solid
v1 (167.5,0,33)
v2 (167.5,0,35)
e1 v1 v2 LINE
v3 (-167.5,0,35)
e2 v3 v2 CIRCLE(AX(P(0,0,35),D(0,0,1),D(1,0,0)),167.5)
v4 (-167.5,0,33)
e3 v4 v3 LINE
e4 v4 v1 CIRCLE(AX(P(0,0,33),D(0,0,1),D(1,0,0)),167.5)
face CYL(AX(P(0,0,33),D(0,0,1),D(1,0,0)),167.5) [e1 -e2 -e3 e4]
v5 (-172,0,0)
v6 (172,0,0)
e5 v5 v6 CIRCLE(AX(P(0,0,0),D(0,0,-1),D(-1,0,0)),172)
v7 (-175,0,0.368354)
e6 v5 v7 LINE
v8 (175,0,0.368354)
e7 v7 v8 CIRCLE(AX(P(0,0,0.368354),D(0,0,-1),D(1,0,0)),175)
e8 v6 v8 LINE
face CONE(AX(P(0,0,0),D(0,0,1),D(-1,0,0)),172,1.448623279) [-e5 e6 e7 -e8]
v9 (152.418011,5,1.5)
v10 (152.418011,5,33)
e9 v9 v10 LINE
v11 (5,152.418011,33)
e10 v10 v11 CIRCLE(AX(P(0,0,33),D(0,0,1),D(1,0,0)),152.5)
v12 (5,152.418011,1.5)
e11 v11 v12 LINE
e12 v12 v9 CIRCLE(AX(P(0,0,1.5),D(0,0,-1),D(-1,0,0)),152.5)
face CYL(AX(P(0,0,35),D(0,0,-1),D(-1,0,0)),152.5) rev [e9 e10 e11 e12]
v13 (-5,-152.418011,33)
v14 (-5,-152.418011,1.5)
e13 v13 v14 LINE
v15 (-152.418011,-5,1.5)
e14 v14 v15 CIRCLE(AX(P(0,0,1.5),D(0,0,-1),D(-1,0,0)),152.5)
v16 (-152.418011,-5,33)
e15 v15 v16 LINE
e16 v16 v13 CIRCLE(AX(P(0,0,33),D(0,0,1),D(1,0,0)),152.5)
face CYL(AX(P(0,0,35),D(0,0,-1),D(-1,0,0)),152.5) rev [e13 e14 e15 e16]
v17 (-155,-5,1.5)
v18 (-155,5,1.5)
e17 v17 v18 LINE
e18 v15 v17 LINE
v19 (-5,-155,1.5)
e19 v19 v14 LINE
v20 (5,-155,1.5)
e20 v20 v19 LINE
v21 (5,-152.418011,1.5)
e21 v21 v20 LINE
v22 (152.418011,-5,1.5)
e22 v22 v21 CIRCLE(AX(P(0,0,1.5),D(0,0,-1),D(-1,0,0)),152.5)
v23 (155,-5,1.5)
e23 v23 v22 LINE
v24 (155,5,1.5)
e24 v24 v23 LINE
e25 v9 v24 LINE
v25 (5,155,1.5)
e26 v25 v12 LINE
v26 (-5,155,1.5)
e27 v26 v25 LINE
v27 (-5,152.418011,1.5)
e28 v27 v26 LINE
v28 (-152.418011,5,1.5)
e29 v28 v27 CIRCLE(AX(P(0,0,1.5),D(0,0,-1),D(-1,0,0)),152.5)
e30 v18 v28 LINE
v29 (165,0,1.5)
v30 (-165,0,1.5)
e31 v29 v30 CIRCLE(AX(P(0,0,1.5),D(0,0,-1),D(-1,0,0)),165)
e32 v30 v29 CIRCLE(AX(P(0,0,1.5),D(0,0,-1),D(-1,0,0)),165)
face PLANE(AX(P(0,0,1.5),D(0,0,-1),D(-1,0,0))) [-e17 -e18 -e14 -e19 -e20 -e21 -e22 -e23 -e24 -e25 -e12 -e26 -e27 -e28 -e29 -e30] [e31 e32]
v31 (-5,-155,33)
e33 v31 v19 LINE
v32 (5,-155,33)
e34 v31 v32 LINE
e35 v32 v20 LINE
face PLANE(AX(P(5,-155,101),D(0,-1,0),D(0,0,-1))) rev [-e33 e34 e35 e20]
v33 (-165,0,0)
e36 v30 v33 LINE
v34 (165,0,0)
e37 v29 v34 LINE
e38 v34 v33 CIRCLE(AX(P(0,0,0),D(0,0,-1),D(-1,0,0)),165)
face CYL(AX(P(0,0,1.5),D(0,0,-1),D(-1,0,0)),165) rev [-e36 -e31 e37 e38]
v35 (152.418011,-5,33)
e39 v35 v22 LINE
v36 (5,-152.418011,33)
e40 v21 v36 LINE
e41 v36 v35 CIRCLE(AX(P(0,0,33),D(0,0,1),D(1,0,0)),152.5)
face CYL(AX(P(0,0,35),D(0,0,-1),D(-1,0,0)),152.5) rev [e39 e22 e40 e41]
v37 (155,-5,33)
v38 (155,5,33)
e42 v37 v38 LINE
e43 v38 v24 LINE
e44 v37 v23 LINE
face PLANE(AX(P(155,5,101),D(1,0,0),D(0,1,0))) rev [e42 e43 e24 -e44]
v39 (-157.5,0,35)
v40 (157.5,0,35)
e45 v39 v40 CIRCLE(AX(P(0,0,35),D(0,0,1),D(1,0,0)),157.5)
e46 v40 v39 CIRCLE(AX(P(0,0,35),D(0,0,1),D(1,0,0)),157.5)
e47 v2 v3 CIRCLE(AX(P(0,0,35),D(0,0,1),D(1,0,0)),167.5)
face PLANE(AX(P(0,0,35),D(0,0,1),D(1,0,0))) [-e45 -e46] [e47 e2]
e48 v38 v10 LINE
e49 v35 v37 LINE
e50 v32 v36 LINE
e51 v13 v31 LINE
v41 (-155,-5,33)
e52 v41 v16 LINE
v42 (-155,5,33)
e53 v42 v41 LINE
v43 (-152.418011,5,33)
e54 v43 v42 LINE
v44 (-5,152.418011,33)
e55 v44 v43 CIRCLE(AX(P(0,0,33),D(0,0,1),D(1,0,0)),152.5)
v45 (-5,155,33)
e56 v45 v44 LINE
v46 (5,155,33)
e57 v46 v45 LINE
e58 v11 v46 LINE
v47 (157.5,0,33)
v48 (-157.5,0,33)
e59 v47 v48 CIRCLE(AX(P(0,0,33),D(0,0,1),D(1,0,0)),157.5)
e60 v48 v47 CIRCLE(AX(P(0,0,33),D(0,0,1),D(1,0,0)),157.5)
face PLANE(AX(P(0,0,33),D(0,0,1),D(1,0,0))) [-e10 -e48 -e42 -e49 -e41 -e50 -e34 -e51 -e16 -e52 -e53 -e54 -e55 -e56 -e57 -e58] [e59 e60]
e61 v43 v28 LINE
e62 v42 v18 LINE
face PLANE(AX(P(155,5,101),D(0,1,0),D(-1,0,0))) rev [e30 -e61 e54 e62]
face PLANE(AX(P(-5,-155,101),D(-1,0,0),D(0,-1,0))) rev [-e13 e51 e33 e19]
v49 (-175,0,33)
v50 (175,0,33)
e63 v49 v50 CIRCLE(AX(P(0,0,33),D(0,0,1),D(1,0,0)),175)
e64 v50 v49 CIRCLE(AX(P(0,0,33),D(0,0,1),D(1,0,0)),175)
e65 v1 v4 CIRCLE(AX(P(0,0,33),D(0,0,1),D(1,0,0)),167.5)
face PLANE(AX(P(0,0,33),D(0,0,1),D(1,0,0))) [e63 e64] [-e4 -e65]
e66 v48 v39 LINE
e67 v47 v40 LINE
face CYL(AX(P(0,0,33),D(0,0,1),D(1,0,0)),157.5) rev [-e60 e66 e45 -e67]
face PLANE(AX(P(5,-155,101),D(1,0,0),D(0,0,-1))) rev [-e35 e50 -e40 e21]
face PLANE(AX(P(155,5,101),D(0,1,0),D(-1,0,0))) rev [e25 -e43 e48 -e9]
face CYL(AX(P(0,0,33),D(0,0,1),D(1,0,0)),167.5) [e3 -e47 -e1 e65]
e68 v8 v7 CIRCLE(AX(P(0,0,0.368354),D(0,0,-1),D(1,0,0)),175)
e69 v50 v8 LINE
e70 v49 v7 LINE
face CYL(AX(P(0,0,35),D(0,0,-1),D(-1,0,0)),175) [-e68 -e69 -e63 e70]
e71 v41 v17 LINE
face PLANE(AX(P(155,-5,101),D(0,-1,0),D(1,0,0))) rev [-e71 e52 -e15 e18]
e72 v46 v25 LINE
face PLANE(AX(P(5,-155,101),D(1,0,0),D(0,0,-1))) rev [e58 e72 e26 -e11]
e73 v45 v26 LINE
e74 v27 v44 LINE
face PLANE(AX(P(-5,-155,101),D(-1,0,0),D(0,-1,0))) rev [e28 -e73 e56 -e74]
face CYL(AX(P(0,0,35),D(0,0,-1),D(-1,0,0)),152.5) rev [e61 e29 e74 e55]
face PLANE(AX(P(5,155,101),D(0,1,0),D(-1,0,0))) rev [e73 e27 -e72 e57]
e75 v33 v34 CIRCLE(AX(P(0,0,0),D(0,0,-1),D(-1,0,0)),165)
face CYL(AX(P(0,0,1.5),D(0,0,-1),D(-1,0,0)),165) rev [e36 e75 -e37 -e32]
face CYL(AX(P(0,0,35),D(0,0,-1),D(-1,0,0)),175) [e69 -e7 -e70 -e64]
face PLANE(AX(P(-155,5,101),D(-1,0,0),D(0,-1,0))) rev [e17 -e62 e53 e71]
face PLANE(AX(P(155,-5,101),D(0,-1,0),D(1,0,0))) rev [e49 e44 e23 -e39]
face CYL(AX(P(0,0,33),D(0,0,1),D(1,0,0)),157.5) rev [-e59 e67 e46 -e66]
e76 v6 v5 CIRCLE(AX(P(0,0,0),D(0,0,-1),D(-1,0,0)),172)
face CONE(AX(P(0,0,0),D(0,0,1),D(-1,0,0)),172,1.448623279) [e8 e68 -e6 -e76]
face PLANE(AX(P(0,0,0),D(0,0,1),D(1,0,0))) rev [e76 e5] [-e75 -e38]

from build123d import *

# Parameters (mm, degrees)
SKETCH1_R           = 175
BOSS_EXTRUDE1_DEPTH = 35
CUT_EXTRUDE1_START  = -2
SKETCH2_R           = 175
SKETCH2_R_2         = 167.5
CUT_EXTRUDE1_DEPTH  = 2
SKETCH3_R           = 157.5
CUT_EXTRUDE2_DEPTH  = 2
SKETCH4_R           = 165
CUT_EXTRUDE3_DEPTH  = 1.5
SKETCH5_R           = 152.5
CUT_EXTRUDE4_DEPTH  = 250.744369306
SKETCH7_W           = 10
SKETCH7_H           = 310
CUT_EXTRUDE6_DEPTH  = 99.5
CIRPATTERN1_COUNT   = 4
SKETCH8_OUTSIDE_W   = 2071.968
SKETCH8_OUTSIDE_H   = 2071.968
SKETCH8_OUTSIDE_R   = 172
CUT_EXTRUDE7_DEPTH  = 99.5
CUT_EXTRUDE7_DRAFT  = -83


with BuildPart() as part:
    # Sketch1 → Boss-Extrude1 (new body)
    with BuildSketch(Plane.XY):
        Circle(SKETCH1_R)
    extrude(amount=BOSS_EXTRUDE1_DEPTH)

    # Sketch2 → Cut-Extrude1 (cut)
    with BuildSketch(Plane.XY.offset(35).offset(CUT_EXTRUDE1_START)):
        Circle(SKETCH2_R)
        Circle(SKETCH2_R_2, mode=Mode.SUBTRACT)
    extrude(amount=CUT_EXTRUDE1_DEPTH, mode=Mode.SUBTRACT)

    # Sketch3 → Cut-Extrude2 (cut)
    with BuildSketch(Plane.XY.offset(35)):
        Circle(SKETCH3_R)
    extrude(amount=-CUT_EXTRUDE2_DEPTH, mode=Mode.SUBTRACT)

    # Sketch4 → Cut-Extrude3 (cut)
    with BuildSketch(Plane(origin=(0, 0, 0), x_dir=(-1, 0, 0), z_dir=(0, 0, -1))):
        Circle(SKETCH4_R)
    extrude(amount=-CUT_EXTRUDE3_DEPTH, mode=Mode.SUBTRACT)

    # Sketch5 → Cut-Extrude4 (cut, through all)
    with BuildSketch(Plane(origin=(0, 0, 1.5), x_dir=(-1, 0, 0), z_dir=(0, 0, -1))):
        Circle(SKETCH5_R)
    extrude(amount=-CUT_EXTRUDE4_DEPTH, mode=Mode.SUBTRACT)

    # Sketch7 → Cut-Extrude6 (cut)
    with BuildSketch(Plane(origin=(0, 0, 1.5), x_dir=(-1, 0, 0), z_dir=(0, 0, -1))):
        Rectangle(SKETCH7_W, SKETCH7_H)
    cut_extrude6 = extrude(amount=-CUT_EXTRUDE6_DEPTH, mode=Mode.SUBTRACT)

    # CirPattern1: Cut-Extrude6 ×4 about axis
    cirpattern1_axis = Axis((0, 0, 0), (0, 0, 1))
    for i in range(1, CIRPATTERN1_COUNT):
        add(cut_extrude6.rotate(cirpattern1_axis, i * 360 / CIRPATTERN1_COUNT), mode=Mode.SUBTRACT)


with BuildPart() as cut_extrude7_tool:
    # Sketch8 outside → Cut-Extrude7 (with draft: the straight prism first)
    with BuildSketch(Plane(origin=(0, 0, 0), x_dir=(-1, 0, 0), z_dir=(0, 0, -1))):
        Rectangle(SKETCH8_OUTSIDE_W, SKETCH8_OUTSIDE_H)
        Circle(SKETCH8_OUTSIDE_R, mode=Mode.SUBTRACT)
    extrude(amount=-CUT_EXTRUDE7_DEPTH)
    # Cut-Extrude7: the draft: its side faces are tilted about the plane it starts from
    cut_extrude7_sides = [cut_extrude7_tool.faces().sort_by_distance(p)[0] for p in [
        (0, -1035.984, 49.75),
        (-1035.984, 0, 49.75),
        (0, 1035.984, 49.75),
        (1035.984, 0, 49.75),
        (172, 0, 49.75),
    ]]
    draft(cut_extrude7_sides, Plane(origin=(0, 0, 0), x_dir=(-1, 0, 0), z_dir=(0, 0, -1)), CUT_EXTRUDE7_DRAFT)


with BuildPart() as part_1:
    add(part.part)

    # Cut-Extrude7: cut by cut_extrude7_tool
    add(cut_extrude7_tool.part, mode=Mode.SUBTRACT)


solid = part_1.part
